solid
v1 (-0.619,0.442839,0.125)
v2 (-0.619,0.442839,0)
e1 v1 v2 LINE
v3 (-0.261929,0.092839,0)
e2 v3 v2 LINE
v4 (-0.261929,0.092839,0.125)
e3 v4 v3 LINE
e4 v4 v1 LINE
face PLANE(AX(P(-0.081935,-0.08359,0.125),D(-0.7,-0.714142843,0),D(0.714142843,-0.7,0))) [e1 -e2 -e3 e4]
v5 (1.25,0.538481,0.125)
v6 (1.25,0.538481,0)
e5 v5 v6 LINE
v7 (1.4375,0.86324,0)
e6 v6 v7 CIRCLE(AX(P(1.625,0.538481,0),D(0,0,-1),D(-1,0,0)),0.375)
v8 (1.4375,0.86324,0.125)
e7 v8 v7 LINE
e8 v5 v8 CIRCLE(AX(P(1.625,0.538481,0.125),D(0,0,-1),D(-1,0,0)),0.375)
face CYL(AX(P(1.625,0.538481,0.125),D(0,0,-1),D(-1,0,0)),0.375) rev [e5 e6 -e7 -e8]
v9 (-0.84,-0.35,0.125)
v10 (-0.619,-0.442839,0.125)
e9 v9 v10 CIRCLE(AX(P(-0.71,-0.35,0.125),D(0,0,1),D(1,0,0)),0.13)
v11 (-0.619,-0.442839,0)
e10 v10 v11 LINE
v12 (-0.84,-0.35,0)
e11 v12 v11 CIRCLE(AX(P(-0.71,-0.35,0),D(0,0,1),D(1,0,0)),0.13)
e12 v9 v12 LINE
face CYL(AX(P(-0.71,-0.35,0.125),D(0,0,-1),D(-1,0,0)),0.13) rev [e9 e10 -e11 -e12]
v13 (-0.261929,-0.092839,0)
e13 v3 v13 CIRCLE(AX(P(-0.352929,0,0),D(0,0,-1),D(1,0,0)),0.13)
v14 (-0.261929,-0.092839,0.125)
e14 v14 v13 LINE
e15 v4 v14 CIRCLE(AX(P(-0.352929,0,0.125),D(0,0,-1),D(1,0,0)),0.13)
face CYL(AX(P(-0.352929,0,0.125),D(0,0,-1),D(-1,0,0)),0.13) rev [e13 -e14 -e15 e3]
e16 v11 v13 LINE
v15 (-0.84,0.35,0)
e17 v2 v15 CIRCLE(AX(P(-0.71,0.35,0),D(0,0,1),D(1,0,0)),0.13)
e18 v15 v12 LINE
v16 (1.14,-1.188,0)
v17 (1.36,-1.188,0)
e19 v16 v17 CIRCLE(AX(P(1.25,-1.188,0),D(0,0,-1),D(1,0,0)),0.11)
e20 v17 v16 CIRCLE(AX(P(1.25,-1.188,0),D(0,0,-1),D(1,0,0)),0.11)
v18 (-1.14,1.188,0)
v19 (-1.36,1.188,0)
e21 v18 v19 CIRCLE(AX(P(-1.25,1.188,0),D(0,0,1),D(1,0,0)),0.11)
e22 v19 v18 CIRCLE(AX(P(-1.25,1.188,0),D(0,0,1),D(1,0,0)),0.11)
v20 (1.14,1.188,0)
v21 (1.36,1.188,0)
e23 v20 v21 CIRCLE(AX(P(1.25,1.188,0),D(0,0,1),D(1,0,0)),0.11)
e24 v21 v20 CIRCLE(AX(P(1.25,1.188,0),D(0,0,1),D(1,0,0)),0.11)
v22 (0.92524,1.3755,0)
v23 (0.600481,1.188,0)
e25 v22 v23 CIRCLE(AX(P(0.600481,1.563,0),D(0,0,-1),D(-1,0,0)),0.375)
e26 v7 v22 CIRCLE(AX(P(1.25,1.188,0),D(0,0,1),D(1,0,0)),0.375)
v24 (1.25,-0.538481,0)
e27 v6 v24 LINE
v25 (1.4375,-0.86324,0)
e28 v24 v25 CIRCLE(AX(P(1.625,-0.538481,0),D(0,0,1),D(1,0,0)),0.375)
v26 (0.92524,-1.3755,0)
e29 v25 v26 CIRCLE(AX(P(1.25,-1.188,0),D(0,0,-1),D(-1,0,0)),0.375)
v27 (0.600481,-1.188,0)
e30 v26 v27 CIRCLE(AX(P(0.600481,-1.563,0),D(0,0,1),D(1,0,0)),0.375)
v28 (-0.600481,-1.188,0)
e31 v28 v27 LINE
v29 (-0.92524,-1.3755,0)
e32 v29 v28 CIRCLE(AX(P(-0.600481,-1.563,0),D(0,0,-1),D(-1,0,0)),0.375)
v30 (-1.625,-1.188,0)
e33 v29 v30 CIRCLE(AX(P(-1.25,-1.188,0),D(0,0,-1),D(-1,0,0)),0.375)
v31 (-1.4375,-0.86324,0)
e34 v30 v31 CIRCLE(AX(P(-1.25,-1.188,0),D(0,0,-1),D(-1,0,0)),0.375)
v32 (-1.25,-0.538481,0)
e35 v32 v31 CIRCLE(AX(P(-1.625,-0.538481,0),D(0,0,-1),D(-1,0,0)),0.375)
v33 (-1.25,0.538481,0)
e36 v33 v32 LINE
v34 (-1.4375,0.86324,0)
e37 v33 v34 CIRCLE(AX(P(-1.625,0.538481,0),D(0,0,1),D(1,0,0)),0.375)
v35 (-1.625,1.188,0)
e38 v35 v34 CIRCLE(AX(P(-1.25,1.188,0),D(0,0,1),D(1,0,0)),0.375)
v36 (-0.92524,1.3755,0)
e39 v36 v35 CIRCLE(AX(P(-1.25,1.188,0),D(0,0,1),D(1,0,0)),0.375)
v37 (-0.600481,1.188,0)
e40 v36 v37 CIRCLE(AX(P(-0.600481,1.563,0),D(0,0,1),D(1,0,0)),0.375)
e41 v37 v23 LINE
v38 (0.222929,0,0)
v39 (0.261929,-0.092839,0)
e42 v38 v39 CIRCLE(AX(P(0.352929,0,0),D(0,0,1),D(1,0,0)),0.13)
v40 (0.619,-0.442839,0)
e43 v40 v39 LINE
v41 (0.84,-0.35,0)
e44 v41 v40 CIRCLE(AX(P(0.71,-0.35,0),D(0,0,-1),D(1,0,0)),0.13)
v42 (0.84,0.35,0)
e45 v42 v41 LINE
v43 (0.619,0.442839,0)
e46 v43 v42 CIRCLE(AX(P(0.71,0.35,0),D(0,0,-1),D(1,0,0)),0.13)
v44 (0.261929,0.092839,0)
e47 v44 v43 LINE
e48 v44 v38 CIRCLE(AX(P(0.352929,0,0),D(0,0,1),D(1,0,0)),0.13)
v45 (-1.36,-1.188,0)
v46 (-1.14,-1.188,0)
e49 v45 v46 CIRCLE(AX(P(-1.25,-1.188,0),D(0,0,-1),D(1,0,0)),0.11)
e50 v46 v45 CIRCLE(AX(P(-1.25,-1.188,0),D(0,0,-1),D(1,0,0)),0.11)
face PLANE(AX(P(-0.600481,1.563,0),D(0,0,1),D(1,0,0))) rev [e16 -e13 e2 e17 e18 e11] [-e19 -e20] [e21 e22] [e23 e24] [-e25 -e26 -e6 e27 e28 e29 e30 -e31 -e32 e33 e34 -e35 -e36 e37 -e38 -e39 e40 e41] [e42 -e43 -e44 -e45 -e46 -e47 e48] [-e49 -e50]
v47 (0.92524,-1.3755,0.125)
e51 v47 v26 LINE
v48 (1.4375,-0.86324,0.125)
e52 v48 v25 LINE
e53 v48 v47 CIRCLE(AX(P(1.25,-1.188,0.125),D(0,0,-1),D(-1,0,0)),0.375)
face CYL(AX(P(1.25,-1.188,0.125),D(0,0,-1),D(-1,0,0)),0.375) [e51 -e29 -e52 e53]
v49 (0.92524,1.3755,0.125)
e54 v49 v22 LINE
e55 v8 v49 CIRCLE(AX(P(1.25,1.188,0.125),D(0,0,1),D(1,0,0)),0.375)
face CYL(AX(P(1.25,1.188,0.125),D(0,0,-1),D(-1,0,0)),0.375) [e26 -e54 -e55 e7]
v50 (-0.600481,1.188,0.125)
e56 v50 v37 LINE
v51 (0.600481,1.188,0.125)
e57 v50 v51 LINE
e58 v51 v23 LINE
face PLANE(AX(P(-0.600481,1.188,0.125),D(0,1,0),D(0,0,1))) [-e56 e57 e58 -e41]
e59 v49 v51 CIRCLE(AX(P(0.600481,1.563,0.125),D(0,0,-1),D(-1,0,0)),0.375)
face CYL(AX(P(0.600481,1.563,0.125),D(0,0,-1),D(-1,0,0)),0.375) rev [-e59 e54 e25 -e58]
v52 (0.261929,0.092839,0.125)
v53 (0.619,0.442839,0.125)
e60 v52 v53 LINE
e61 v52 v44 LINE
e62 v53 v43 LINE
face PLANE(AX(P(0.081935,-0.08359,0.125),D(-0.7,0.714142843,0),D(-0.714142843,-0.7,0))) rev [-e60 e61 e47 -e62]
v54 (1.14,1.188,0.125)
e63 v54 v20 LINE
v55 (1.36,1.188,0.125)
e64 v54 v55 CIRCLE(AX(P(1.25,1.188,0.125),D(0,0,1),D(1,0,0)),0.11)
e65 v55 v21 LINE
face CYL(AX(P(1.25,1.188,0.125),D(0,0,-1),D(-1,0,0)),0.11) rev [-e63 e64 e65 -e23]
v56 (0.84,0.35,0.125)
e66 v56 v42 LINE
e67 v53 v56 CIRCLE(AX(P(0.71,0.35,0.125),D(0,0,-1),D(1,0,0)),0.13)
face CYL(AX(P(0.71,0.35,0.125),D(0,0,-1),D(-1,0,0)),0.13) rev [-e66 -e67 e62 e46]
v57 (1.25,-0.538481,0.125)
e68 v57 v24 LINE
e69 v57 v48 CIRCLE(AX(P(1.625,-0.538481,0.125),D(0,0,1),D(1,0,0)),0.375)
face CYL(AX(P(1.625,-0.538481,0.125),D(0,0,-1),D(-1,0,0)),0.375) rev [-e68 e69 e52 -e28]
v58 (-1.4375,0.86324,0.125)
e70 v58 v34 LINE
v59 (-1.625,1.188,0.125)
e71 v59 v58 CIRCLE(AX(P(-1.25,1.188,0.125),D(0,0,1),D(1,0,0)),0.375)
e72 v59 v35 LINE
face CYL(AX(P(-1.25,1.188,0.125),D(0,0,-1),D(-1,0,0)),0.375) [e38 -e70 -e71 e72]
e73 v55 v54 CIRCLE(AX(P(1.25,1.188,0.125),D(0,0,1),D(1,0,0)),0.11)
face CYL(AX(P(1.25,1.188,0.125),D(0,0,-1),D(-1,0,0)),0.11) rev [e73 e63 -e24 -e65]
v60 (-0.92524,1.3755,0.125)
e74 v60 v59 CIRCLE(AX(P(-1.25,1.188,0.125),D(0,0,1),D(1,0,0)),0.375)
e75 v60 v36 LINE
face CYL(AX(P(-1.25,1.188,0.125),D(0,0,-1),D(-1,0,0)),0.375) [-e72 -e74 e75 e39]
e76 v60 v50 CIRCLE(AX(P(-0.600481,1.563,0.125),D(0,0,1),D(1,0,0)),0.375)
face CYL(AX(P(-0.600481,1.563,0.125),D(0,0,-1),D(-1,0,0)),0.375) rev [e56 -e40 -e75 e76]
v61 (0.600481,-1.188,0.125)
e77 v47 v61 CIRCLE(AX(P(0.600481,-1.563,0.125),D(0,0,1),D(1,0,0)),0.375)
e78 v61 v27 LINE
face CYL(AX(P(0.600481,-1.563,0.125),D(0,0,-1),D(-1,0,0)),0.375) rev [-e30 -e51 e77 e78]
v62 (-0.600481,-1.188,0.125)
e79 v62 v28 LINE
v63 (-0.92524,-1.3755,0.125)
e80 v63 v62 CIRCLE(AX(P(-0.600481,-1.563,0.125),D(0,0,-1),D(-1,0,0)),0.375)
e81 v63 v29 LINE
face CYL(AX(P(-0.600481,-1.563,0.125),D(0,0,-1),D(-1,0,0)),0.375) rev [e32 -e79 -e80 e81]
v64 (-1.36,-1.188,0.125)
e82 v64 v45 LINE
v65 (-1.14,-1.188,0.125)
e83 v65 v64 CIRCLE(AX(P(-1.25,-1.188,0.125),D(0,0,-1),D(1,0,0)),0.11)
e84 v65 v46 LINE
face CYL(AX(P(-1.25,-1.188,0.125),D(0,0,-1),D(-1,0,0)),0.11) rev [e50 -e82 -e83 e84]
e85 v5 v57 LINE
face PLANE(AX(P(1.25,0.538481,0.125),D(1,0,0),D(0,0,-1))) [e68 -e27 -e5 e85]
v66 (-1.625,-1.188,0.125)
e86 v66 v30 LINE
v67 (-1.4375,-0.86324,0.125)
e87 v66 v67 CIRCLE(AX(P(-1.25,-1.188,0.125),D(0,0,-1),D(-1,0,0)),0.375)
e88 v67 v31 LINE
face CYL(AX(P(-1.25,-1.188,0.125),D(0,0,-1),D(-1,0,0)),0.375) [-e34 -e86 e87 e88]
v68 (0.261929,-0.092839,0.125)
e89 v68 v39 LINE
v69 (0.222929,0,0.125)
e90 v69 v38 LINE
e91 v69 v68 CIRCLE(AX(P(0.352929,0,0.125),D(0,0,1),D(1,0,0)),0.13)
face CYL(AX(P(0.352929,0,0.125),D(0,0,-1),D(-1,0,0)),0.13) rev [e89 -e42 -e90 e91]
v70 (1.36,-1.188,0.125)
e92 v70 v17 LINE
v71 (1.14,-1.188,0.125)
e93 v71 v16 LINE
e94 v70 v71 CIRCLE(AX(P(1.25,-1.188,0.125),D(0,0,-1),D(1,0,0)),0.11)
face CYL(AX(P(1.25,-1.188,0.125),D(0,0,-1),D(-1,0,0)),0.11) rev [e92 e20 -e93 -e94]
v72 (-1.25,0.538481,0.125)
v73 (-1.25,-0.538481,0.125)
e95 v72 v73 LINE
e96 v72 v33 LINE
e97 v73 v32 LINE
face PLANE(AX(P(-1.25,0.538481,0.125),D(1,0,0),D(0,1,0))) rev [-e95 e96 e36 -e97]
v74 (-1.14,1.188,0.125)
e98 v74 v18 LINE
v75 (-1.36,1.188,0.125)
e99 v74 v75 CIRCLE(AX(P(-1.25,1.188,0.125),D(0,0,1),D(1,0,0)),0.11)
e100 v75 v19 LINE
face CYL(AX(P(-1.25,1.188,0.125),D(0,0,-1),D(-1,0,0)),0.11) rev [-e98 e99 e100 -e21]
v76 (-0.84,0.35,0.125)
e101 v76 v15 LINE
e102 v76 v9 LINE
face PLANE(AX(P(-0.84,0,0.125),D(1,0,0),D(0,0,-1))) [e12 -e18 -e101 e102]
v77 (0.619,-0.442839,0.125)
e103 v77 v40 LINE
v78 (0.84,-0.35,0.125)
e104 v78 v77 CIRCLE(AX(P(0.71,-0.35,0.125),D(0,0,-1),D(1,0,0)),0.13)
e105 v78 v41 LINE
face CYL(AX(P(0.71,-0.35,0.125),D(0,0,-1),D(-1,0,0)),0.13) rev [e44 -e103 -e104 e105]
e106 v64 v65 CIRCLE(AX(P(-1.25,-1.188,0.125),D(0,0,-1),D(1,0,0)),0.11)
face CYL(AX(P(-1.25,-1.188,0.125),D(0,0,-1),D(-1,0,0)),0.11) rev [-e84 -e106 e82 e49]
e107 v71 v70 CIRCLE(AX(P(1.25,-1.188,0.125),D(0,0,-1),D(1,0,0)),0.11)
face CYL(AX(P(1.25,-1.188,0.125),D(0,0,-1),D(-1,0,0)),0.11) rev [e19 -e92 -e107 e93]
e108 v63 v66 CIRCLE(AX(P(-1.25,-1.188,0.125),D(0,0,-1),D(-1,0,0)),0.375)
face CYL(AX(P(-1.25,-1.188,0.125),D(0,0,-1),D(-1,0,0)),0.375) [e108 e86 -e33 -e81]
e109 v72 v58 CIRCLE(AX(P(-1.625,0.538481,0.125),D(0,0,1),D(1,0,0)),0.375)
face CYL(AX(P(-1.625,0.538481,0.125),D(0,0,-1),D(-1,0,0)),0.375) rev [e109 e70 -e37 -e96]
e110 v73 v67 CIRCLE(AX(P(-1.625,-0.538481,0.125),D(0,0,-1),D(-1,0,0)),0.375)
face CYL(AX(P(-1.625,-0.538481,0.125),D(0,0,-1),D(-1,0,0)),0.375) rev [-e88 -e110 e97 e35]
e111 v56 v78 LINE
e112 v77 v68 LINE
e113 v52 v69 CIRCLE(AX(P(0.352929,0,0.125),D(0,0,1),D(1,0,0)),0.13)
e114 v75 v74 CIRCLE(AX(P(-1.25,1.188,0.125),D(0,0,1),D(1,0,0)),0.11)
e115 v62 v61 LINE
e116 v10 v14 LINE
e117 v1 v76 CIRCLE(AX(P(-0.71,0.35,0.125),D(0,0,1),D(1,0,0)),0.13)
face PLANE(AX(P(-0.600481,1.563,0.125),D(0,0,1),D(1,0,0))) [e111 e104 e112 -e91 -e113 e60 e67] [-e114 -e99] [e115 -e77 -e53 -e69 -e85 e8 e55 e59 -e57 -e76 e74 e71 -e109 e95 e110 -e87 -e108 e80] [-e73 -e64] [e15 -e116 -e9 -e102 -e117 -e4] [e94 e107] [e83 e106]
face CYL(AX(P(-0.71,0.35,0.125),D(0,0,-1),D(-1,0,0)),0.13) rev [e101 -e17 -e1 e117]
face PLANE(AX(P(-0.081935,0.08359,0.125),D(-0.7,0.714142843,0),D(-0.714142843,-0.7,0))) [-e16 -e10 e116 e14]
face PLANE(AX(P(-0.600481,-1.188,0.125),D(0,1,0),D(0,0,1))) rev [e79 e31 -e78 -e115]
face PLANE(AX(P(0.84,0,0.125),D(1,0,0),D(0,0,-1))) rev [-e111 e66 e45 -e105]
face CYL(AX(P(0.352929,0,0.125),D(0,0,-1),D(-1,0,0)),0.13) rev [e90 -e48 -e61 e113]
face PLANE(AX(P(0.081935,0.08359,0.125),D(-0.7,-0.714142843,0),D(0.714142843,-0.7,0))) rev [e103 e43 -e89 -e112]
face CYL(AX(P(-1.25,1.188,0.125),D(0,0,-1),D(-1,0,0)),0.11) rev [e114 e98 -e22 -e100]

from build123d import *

# Parameters (mm, degrees)
BRACKET_PLATE_PROFILE_R = 0.11
BRACKET_PLATE_DEPTH     = 0.125


with BuildPart() as part:
    # Bracket Plate Profile → Bracket Plate (new body)
    with BuildSketch(Plane.XY):
        with BuildLine():
            Line((-1.25, 0.538480947), (-1.25, -0.538480947))
            ThreePointArc((-1.25, -0.538480947), (-1.300240474, -0.725980947), (-1.4375, -0.863240474))
            ThreePointArc((-1.4375, -0.863240474), (-1.515165043, -1.453165043), (-0.925240474, -1.3755))
            ThreePointArc((-0.925240474, -1.3755), (-0.787980947, -1.238240474), (-0.600480947, -1.188))
            Line((-0.600480947, -1.188), (0.600480947, -1.188))
            ThreePointArc((0.600480947, -1.188), (0.787980947, -1.238240474), (0.925240474, -1.3755))
            ThreePointArc((0.925240474, -1.3755), (1.515165043, -1.453165043), (1.4375, -0.863240474))
            ThreePointArc((1.4375, -0.863240474), (1.300240474, -0.725980947), (1.25, -0.538480947))
            Line((1.25, -0.538480947), (1.25, 0.538480947))
            ThreePointArc((1.25, 0.538480947), (1.300240474, 0.725980947), (1.4375, 0.863240474))
            ThreePointArc((1.4375, 0.863240474), (1.515165043, 1.453165043), (0.925240474, 1.3755))
            ThreePointArc((0.925240474, 1.3755), (0.787980947, 1.238240474), (0.600480947, 1.188))
            Line((0.600480947, 1.188), (-0.600480947, 1.188))
            ThreePointArc((-0.600480947, 1.188), (-0.787980947, 1.238240474), (-0.925240474, 1.3755))
            ThreePointArc((-0.925240474, 1.3755), (-1.515165043, 1.453165043), (-1.4375, 0.863240474))
            ThreePointArc((-1.4375, 0.863240474), (-1.300240474, 0.725980947), (-1.25, 0.538480947))
        make_face()
        with Locations((-1.25, 1.188)):
            Circle(BRACKET_PLATE_PROFILE_R, mode=Mode.SUBTRACT)
        with Locations((1.25, 1.188)):
            Circle(BRACKET_PLATE_PROFILE_R, mode=Mode.SUBTRACT)
        with Locations((1.25, -1.188)):
            Circle(BRACKET_PLATE_PROFILE_R, mode=Mode.SUBTRACT)
        with Locations((-1.25, -1.188)):
            Circle(BRACKET_PLATE_PROFILE_R, mode=Mode.SUBTRACT)
        with BuildLine():
            Line((-0.84, 0.35), (-0.84, -0.35))
            ThreePointArc((-0.84, -0.35), (-0.760348784, -0.469854078), (-0.619, -0.44283857))
            Line((-0.619, -0.44283857), (-0.261928579, -0.09283857))
            ThreePointArc((-0.261928579, -0.09283857), (-0.222928579, 0), (-0.261928579, 0.09283857))
            Line((-0.261928579, 0.09283857), (-0.619, 0.44283857))
            ThreePointArc((-0.619, 0.44283857), (-0.760348784, 0.469854078), (-0.84, 0.35))
        make_face(mode=Mode.SUBTRACT)
        with BuildLine():
            Line((0.619, -0.44283857), (0.261928579, -0.09283857))
            ThreePointArc((0.261928579, -0.09283857), (0.222928579, 0), (0.261928579, 0.09283857))
            Line((0.261928579, 0.09283857), (0.619, 0.44283857))
            ThreePointArc((0.619, 0.44283857), (0.760348784, 0.469854078), (0.84, 0.35))
            Line((0.84, 0.35), (0.84, -0.35))
            ThreePointArc((0.84, -0.35), (0.760348784, -0.469854078), (0.619, -0.44283857))
        make_face(mode=Mode.SUBTRACT)
    extrude(amount=BRACKET_PLATE_DEPTH)


solid = part.part
